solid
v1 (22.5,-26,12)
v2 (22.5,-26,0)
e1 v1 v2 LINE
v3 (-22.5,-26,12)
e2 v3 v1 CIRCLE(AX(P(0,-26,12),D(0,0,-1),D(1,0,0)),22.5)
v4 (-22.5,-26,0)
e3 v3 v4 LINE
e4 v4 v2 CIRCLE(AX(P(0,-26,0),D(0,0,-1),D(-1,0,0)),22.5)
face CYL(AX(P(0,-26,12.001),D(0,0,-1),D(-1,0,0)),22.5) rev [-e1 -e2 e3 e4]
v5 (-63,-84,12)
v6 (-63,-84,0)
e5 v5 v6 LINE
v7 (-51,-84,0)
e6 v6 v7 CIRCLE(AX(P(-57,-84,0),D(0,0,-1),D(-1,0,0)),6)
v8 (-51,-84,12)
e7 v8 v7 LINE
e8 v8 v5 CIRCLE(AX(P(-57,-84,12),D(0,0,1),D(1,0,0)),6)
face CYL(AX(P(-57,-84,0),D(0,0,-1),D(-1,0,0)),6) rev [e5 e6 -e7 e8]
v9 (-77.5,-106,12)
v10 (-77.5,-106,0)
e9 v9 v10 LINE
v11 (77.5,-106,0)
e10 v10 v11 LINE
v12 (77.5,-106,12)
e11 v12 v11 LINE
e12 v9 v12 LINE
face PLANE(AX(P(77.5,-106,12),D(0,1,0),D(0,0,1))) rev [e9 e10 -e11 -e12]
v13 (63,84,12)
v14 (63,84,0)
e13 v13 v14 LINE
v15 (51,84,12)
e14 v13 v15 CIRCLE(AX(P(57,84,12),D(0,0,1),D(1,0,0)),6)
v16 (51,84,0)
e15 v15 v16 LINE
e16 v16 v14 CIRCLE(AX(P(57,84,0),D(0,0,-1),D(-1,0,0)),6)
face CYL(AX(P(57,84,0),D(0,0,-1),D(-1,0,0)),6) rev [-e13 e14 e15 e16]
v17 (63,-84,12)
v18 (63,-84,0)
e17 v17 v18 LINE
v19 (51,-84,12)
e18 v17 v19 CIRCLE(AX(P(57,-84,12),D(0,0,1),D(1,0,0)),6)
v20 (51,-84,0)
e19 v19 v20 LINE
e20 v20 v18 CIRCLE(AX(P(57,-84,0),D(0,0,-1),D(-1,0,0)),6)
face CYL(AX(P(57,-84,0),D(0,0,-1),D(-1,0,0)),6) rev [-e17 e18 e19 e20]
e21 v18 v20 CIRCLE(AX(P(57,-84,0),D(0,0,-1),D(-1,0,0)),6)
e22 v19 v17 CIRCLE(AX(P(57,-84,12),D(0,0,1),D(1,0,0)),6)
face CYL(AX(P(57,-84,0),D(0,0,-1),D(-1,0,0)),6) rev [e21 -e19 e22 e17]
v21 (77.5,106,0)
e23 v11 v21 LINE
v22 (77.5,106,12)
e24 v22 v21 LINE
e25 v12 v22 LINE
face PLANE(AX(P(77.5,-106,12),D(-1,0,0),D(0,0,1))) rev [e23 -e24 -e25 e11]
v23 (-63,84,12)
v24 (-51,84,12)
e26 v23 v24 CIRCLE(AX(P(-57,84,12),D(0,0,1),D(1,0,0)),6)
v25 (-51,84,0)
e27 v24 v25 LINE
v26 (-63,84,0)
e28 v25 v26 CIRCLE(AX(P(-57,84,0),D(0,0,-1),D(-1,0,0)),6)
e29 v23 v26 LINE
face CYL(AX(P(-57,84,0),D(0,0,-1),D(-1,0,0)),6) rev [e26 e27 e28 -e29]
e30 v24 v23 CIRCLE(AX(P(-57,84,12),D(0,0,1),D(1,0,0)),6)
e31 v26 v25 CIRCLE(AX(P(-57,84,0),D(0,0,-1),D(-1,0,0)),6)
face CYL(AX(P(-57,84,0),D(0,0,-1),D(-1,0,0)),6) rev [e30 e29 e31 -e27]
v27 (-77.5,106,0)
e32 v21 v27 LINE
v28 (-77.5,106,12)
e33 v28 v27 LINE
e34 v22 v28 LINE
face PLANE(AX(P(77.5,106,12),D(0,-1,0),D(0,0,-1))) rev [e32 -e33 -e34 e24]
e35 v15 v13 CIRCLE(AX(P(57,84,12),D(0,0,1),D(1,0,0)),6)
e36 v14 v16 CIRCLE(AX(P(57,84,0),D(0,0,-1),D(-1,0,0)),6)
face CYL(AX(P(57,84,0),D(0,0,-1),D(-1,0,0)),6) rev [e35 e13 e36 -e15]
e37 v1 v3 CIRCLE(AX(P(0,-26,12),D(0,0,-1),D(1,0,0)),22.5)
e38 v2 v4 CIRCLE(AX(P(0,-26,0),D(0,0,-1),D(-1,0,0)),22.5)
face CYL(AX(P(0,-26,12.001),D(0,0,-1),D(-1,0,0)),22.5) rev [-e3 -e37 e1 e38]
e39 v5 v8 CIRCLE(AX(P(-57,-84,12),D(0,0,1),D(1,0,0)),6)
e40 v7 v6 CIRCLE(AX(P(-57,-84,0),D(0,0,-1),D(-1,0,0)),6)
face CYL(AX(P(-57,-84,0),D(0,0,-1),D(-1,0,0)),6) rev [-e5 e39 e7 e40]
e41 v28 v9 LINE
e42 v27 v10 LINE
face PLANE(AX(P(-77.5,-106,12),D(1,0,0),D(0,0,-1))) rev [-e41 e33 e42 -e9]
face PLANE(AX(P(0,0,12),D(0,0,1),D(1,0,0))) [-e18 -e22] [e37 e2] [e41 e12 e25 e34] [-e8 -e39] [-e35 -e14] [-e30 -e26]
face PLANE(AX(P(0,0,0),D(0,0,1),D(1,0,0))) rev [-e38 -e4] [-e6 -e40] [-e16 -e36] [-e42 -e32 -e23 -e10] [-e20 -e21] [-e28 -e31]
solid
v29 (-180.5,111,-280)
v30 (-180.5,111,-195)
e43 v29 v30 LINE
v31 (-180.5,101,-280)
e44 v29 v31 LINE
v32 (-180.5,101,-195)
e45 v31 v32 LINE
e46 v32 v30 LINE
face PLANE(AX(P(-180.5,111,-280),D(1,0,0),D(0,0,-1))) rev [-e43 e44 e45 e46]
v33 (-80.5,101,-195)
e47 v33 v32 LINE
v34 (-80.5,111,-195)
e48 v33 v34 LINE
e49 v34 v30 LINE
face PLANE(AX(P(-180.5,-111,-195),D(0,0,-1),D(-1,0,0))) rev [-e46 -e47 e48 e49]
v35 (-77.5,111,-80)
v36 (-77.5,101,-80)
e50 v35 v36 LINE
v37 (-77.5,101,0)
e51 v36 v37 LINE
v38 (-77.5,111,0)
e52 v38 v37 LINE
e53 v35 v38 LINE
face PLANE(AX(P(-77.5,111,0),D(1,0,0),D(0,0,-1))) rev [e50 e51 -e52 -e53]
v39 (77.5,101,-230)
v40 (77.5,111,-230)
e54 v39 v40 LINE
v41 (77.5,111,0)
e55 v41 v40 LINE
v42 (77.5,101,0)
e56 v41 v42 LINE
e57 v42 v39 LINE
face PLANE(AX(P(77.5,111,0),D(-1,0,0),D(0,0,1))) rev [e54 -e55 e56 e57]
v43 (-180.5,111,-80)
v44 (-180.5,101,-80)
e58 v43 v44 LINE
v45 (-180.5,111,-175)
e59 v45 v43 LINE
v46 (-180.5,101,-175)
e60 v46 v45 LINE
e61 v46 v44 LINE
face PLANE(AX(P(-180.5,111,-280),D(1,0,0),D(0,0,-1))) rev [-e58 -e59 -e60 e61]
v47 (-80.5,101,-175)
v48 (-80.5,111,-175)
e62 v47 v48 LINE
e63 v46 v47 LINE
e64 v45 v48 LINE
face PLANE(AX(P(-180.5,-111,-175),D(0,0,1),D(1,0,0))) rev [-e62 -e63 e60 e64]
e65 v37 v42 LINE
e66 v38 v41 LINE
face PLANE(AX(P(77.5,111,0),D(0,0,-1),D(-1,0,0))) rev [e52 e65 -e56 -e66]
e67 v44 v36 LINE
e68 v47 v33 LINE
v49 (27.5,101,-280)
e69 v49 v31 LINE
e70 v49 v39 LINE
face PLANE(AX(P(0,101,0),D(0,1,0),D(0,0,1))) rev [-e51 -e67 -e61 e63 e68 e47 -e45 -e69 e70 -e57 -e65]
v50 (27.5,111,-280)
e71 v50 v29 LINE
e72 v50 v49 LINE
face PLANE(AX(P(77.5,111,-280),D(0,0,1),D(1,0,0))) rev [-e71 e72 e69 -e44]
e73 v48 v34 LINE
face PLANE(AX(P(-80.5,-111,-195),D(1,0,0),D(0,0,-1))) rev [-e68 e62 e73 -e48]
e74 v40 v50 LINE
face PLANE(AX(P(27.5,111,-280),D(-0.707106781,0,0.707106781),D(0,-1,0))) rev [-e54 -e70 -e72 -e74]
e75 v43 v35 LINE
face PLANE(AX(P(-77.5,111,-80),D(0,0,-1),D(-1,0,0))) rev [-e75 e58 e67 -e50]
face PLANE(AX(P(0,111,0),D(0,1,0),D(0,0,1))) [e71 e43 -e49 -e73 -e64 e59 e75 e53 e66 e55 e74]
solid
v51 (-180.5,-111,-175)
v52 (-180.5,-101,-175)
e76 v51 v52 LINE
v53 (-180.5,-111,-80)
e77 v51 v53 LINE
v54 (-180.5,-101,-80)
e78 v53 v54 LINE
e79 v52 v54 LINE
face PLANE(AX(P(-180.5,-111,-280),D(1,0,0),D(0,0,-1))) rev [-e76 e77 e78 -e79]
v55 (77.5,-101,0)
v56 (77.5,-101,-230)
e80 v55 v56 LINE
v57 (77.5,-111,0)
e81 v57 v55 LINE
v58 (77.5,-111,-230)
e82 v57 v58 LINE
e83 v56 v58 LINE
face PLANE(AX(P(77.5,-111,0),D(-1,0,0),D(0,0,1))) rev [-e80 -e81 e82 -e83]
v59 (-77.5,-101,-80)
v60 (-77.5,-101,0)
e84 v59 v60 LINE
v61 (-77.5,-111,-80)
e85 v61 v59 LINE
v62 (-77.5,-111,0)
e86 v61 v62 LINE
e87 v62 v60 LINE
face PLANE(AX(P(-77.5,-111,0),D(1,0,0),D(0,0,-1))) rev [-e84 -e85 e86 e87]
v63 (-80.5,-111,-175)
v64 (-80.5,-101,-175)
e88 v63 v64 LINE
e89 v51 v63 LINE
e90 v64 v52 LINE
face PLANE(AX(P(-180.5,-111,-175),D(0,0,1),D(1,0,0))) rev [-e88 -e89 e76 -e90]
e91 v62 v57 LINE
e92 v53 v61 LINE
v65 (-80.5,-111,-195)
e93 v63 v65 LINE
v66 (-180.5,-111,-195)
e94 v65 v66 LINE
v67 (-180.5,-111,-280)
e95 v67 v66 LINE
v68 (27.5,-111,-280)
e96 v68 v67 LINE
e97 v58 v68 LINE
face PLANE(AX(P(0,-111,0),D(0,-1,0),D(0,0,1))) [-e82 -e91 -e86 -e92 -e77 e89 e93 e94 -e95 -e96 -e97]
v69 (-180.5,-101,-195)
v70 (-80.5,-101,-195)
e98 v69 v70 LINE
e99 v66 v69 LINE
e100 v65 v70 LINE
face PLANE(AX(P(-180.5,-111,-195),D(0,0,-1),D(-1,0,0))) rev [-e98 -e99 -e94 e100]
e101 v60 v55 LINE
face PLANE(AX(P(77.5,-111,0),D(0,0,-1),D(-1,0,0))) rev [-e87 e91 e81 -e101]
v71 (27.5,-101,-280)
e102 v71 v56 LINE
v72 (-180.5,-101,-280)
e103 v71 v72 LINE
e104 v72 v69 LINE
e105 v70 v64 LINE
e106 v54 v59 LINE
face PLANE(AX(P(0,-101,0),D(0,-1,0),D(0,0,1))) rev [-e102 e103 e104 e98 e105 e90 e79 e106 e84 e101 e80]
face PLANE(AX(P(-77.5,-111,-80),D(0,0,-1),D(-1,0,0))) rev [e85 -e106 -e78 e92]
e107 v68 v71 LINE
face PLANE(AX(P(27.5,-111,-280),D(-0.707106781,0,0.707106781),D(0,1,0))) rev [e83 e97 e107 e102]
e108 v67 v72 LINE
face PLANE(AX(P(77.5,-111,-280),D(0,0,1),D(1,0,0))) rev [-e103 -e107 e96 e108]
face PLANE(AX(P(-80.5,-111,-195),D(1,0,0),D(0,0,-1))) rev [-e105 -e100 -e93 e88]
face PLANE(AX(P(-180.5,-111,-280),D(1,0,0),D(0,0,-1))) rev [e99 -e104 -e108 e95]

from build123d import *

# Parameters (mm, degrees)
SKETCH1_W                  = 155
SKETCH1_H                  = 212
BOSS_EXTRUDE1_DEPTH        = 12
F_12_0_12_DIAMETER_HOLE1_D = 12
BOSS_EXTRUDE2_DEPTH        = 5
CHAMFER1_SIZE              = 50
SKETCH9_R                  = 22.5
CUT_EXTRUDE2_DEPTH         = 12
SKETCH10_W                 = 100
SKETCH10_H                 = 20
CUT_EXTRUDE3_DEPTH         = 401.33017623


with BuildPart() as part:
    # Sketch1 → Boss-Extrude1 (new body)
    with BuildSketch(Plane.XY):
        Rectangle(SKETCH1_W, SKETCH1_H)
    extrude(amount=BOSS_EXTRUDE1_DEPTH)

    # Ø12.0 (12) Diameter Hole1 (through all)
    with Locations(Plane(origin=(0, 0, 0), x_dir=(-1, 0, 0), z_dir=(0, 0, -1))):
        with Locations((-57, 84), (57, 84), (-57, -84), (57, -84)):
            Hole(F_12_0_12_DIAMETER_HOLE1_D / 2)

    # Sketch9 → Cut-Extrude2 (cut)
    with BuildSketch(Plane(origin=(0, 0, 0), x_dir=(-1, 0, 0), z_dir=(0, 0, -1))):
        with Locations((0, -26)):
            Circle(SKETCH9_R)
    extrude(amount=-CUT_EXTRUDE2_DEPTH, mode=Mode.SUBTRACT)


with BuildPart() as body_2:
    # Sketch8 → Boss-Extrude2 (new, symmetric)
    with BuildSketch(Plane(origin=(0, 106, 0), x_dir=(1, 0, 0), z_dir=(0, 1, 0))):
        Polygon((77.5, 0), (-77.5, 0), (-77.5, 80), (-180.5, 80), (-180.5, 280), (77.5, 280), align=None)
    extrude(amount=BOSS_EXTRUDE2_DEPTH, both=True)

    # Chamfer1
    chamfer1_edges = [body_2.edges().sort_by_distance(p)[0] for p in [
        (77.5, 106, -280),
    ]]
    chamfer(chamfer1_edges, length=CHAMFER1_SIZE)


with BuildPart() as body_3:
    # Mirror1: mirrored copy
    add(body_2.part.mirror(Plane.ZX))


with BuildPart() as cut_extrude3_tool:
    # Sketch10 → Cut-Extrude3 (new, through all)
    with BuildSketch(Plane(origin=(0, 111, 0), x_dir=(1, 0, 0), z_dir=(0, 1, 0))):
        with Locations((-130.5, 185)):
            Rectangle(SKETCH10_W, SKETCH10_H)
    extrude(amount=-CUT_EXTRUDE3_DEPTH)


with BuildPart() as body_2_1:
    add(body_2.part)

    # Cut-Extrude3: cut by cut_extrude3_tool
    add(cut_extrude3_tool.part, mode=Mode.SUBTRACT)


with BuildPart() as body_3_1:
    add(body_3.part)

    # Cut-Extrude3: cut by cut_extrude3_tool
    add(cut_extrude3_tool.part, mode=Mode.SUBTRACT)


solid = Compound([part.part, body_2_1.part, body_3_1.part])
